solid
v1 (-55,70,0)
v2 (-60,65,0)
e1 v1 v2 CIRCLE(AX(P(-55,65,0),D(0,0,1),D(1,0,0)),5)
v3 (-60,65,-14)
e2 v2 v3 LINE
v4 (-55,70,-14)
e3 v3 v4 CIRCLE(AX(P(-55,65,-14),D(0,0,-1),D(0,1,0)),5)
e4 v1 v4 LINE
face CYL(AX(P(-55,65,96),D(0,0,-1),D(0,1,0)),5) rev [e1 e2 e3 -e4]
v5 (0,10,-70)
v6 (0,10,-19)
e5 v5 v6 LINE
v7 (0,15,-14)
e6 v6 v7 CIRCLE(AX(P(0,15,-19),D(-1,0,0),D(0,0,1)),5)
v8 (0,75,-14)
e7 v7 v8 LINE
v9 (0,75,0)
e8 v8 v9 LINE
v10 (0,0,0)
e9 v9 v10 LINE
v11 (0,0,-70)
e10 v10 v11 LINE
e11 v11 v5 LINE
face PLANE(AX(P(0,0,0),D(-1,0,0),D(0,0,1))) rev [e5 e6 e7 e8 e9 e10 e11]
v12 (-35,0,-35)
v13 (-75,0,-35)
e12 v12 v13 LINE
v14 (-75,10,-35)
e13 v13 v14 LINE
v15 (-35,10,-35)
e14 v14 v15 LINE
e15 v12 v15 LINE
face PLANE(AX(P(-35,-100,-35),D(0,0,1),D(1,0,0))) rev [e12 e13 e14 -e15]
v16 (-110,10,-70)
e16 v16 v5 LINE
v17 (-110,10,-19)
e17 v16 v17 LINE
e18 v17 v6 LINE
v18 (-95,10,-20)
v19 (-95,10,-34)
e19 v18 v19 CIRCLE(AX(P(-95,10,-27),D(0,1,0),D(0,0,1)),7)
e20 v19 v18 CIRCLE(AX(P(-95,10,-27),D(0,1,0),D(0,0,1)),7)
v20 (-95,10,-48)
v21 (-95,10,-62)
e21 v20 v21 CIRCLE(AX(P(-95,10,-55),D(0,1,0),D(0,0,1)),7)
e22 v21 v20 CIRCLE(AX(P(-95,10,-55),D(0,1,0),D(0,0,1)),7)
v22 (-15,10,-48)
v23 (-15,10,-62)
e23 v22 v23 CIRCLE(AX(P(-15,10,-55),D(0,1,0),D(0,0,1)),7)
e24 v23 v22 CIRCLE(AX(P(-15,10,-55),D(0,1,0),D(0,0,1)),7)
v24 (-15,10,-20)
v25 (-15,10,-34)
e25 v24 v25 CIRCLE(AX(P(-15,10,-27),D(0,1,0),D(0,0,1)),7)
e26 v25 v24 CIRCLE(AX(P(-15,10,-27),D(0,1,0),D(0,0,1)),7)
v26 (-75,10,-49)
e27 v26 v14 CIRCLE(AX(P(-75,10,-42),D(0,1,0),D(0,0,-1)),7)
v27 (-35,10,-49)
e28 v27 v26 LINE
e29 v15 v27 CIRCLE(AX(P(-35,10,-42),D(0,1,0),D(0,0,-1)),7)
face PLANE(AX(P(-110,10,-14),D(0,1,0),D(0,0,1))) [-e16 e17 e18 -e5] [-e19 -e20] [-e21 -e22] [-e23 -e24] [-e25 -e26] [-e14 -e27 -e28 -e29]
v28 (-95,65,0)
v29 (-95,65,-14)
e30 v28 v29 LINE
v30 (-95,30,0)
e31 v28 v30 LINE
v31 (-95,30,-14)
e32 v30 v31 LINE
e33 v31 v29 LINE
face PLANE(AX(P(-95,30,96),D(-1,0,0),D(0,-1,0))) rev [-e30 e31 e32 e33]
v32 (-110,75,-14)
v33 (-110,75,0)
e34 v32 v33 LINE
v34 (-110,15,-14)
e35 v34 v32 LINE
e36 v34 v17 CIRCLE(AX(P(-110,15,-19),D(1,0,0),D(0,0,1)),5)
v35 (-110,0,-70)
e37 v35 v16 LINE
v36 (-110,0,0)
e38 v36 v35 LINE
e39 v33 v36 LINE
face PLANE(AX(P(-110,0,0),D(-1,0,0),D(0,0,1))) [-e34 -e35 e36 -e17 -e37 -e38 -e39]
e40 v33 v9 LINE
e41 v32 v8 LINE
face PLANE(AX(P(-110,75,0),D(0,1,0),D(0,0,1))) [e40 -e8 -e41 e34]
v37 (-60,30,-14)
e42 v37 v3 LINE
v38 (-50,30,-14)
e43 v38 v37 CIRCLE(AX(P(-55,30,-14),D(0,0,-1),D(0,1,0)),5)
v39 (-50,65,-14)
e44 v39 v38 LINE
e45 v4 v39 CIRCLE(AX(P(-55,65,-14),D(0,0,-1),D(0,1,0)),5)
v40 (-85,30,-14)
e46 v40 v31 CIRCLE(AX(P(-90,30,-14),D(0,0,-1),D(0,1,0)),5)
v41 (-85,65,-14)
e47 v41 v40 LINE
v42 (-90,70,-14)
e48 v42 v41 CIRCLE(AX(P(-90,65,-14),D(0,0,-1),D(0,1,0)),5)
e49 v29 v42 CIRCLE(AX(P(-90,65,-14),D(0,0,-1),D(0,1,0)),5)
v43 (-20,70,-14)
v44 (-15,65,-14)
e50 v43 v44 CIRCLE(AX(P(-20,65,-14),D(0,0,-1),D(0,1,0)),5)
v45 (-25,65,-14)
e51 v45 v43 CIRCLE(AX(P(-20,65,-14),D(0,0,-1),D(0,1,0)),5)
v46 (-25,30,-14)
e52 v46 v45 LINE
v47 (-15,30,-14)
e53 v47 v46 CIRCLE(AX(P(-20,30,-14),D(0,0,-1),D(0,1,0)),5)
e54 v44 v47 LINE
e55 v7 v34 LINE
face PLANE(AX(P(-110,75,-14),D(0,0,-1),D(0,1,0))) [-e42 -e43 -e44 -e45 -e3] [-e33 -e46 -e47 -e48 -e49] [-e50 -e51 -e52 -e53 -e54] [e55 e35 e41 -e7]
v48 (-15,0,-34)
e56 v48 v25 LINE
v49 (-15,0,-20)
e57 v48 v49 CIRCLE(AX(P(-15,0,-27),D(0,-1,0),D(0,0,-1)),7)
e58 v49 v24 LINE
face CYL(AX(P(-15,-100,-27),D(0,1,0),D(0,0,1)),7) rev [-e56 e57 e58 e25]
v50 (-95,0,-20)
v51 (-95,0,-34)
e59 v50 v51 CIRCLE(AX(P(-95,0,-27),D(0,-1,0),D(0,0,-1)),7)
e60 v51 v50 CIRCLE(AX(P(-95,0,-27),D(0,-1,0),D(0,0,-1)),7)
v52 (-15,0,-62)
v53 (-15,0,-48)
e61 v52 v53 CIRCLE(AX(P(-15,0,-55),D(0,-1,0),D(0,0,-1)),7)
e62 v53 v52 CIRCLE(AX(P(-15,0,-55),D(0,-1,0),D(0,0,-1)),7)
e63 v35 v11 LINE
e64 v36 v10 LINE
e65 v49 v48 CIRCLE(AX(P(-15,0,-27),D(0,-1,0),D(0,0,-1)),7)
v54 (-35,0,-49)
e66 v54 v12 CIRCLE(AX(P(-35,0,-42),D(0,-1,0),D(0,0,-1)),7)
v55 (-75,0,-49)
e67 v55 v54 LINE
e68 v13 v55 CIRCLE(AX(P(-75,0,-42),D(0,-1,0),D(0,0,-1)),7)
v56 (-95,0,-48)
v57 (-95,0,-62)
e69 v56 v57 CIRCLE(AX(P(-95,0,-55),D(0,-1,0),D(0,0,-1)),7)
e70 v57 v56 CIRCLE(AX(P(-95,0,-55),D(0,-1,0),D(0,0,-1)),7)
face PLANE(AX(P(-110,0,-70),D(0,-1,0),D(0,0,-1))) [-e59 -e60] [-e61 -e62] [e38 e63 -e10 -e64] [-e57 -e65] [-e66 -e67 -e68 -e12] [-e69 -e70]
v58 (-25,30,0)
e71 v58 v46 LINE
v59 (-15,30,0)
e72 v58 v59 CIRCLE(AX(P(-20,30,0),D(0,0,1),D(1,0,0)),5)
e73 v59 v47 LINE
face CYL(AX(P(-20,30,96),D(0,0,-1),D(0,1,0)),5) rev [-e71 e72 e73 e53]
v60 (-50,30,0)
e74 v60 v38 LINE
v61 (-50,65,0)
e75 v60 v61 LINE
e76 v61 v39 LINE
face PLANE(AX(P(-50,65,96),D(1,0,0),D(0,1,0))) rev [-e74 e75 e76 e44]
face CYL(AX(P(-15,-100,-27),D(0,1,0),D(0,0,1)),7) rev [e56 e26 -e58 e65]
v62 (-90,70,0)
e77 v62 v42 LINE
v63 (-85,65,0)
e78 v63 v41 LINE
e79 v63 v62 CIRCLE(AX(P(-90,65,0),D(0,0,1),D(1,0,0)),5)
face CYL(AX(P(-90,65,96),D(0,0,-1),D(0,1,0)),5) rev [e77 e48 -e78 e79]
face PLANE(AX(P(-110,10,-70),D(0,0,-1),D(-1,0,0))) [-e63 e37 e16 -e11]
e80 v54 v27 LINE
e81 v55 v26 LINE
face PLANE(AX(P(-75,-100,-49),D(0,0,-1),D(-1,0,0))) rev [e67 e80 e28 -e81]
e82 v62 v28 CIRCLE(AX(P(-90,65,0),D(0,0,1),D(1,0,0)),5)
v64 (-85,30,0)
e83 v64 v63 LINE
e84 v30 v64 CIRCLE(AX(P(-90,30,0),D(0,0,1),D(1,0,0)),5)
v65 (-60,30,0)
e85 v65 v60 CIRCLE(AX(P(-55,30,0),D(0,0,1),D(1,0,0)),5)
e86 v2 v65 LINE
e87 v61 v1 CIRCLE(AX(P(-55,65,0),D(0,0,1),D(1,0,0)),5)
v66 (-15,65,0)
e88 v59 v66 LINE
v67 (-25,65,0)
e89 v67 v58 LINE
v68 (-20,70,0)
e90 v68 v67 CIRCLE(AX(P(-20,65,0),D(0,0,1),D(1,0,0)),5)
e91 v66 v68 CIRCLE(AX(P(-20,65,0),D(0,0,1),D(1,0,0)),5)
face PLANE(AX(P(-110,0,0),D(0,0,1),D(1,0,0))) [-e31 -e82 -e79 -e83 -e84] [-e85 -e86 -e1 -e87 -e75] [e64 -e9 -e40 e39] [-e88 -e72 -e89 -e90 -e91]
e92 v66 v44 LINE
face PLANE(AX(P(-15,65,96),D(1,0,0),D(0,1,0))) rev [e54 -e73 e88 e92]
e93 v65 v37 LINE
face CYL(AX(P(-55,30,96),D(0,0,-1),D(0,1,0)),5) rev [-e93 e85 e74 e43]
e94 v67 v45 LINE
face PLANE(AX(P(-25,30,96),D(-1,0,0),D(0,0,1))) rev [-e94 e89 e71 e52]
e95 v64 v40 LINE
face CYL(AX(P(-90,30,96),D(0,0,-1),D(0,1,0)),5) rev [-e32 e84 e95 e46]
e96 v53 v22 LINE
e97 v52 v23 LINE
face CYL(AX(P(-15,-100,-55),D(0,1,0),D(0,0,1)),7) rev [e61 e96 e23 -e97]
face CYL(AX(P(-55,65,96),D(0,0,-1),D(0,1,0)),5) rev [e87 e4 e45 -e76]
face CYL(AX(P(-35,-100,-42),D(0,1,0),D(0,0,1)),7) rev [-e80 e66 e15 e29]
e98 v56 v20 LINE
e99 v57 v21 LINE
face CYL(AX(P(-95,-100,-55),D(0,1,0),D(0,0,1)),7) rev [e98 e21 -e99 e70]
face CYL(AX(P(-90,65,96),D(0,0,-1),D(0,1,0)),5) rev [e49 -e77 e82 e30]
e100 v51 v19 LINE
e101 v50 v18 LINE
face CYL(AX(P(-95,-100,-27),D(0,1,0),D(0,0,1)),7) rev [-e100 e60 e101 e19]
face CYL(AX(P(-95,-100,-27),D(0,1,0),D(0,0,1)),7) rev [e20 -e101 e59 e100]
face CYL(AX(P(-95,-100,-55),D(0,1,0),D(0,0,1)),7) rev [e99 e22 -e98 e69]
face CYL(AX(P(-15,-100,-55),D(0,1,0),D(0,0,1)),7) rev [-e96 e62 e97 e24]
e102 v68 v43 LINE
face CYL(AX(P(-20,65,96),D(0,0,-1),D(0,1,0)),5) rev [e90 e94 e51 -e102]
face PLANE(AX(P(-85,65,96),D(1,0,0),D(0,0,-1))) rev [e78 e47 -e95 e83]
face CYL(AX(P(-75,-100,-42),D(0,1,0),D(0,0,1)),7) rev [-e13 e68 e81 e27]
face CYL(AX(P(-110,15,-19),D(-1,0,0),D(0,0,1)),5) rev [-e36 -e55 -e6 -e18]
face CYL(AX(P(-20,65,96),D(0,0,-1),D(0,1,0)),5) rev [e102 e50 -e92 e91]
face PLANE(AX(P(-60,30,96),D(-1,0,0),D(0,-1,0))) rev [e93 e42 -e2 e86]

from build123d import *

# Parameters (mm, degrees)
L_BRACKET_BODY_DEPTH          = 110
VERTICAL_LEG_SLOTS_3X10_DEPTH = 110
BASE_HOLES_SKETCH_R           = 7
BASE_MOUNTING_HOLES_DEPTH     = 110
INNER_CORNER_FILLET_R5_R      = 5


with BuildPart() as part:
    # Bracket L-Profile Sketch → L-Bracket Body (new body)
    with BuildSketch(Plane(origin=(0, 0, 0), x_dir=(0, 0, -1), z_dir=(1, 0, 0))):
        Polygon((0, 0), (0, 75), (14, 75), (14, 10), (70, 10), (70, 0), align=None)
    extrude(amount=-L_BRACKET_BODY_DEPTH)

    # Vertical Leg Slots Sketch → Vertical Leg Slots 3x10 (cut)
    with BuildSketch(Plane(origin=(0, 0, -14), x_dir=(-1, 0, 0), z_dir=(0, 0, -1))):
        with BuildLine():
            Line((15, 65), (15, 30))
            ThreePointArc((15, 30), (20, 25), (25, 30))
            Line((25, 30), (25, 65))
            ThreePointArc((25, 65), (20, 70), (15, 65))
        make_face()
        with BuildLine():
            Line((50, 65), (50, 30))
            ThreePointArc((50, 30), (55, 25), (60, 30))
            Line((60, 30), (60, 65))
            ThreePointArc((60, 65), (55, 70), (50, 65))
        make_face()
        with BuildLine():
            Line((85, 65), (85, 30))
            ThreePointArc((85, 30), (90, 25), (95, 30))
            Line((95, 30), (95, 65))
            ThreePointArc((95, 65), (90, 70), (85, 65))
        make_face()
    extrude(amount=-VERTICAL_LEG_SLOTS_3X10_DEPTH, mode=Mode.SUBTRACT)

    # Base Holes Sketch → Base Mounting Holes (cut)
    with BuildSketch(Plane(origin=(0, 10, 0), x_dir=(1, 0, 0), z_dir=(0, 1, 0))):
        with Locations(Location((-95, 55, 0), (0, 0, 270))):
            Circle(BASE_HOLES_SKETCH_R)
        with Locations(Location((-15, 55, 0), (0, 0, 270))):
            Circle(BASE_HOLES_SKETCH_R)
        with Locations(Location((-15, 27, 0), (0, 0, 270))):
            Circle(BASE_HOLES_SKETCH_R)
        with Locations(Location((-95, 27, 0), (0, 0, 270))):
            Circle(BASE_HOLES_SKETCH_R)
        with BuildLine():
            Line((-75, 49), (-35, 49))
            ThreePointArc((-35, 49), (-28, 42), (-35, 35))
            Line((-35, 35), (-75, 35))
            ThreePointArc((-75, 35), (-82, 42), (-75, 49))
        make_face()
    extrude(amount=-BASE_MOUNTING_HOLES_DEPTH, mode=Mode.SUBTRACT)

    # Inner Corner Fillet R5
    inner_corner_fillet_r5_edges = [part.edges().sort_by_distance(p)[0] for p in [
        (-55, 10, -14),
    ]]
    fillet(inner_corner_fillet_r5_edges, radius=INNER_CORNER_FILLET_R5_R)


solid = part.part
